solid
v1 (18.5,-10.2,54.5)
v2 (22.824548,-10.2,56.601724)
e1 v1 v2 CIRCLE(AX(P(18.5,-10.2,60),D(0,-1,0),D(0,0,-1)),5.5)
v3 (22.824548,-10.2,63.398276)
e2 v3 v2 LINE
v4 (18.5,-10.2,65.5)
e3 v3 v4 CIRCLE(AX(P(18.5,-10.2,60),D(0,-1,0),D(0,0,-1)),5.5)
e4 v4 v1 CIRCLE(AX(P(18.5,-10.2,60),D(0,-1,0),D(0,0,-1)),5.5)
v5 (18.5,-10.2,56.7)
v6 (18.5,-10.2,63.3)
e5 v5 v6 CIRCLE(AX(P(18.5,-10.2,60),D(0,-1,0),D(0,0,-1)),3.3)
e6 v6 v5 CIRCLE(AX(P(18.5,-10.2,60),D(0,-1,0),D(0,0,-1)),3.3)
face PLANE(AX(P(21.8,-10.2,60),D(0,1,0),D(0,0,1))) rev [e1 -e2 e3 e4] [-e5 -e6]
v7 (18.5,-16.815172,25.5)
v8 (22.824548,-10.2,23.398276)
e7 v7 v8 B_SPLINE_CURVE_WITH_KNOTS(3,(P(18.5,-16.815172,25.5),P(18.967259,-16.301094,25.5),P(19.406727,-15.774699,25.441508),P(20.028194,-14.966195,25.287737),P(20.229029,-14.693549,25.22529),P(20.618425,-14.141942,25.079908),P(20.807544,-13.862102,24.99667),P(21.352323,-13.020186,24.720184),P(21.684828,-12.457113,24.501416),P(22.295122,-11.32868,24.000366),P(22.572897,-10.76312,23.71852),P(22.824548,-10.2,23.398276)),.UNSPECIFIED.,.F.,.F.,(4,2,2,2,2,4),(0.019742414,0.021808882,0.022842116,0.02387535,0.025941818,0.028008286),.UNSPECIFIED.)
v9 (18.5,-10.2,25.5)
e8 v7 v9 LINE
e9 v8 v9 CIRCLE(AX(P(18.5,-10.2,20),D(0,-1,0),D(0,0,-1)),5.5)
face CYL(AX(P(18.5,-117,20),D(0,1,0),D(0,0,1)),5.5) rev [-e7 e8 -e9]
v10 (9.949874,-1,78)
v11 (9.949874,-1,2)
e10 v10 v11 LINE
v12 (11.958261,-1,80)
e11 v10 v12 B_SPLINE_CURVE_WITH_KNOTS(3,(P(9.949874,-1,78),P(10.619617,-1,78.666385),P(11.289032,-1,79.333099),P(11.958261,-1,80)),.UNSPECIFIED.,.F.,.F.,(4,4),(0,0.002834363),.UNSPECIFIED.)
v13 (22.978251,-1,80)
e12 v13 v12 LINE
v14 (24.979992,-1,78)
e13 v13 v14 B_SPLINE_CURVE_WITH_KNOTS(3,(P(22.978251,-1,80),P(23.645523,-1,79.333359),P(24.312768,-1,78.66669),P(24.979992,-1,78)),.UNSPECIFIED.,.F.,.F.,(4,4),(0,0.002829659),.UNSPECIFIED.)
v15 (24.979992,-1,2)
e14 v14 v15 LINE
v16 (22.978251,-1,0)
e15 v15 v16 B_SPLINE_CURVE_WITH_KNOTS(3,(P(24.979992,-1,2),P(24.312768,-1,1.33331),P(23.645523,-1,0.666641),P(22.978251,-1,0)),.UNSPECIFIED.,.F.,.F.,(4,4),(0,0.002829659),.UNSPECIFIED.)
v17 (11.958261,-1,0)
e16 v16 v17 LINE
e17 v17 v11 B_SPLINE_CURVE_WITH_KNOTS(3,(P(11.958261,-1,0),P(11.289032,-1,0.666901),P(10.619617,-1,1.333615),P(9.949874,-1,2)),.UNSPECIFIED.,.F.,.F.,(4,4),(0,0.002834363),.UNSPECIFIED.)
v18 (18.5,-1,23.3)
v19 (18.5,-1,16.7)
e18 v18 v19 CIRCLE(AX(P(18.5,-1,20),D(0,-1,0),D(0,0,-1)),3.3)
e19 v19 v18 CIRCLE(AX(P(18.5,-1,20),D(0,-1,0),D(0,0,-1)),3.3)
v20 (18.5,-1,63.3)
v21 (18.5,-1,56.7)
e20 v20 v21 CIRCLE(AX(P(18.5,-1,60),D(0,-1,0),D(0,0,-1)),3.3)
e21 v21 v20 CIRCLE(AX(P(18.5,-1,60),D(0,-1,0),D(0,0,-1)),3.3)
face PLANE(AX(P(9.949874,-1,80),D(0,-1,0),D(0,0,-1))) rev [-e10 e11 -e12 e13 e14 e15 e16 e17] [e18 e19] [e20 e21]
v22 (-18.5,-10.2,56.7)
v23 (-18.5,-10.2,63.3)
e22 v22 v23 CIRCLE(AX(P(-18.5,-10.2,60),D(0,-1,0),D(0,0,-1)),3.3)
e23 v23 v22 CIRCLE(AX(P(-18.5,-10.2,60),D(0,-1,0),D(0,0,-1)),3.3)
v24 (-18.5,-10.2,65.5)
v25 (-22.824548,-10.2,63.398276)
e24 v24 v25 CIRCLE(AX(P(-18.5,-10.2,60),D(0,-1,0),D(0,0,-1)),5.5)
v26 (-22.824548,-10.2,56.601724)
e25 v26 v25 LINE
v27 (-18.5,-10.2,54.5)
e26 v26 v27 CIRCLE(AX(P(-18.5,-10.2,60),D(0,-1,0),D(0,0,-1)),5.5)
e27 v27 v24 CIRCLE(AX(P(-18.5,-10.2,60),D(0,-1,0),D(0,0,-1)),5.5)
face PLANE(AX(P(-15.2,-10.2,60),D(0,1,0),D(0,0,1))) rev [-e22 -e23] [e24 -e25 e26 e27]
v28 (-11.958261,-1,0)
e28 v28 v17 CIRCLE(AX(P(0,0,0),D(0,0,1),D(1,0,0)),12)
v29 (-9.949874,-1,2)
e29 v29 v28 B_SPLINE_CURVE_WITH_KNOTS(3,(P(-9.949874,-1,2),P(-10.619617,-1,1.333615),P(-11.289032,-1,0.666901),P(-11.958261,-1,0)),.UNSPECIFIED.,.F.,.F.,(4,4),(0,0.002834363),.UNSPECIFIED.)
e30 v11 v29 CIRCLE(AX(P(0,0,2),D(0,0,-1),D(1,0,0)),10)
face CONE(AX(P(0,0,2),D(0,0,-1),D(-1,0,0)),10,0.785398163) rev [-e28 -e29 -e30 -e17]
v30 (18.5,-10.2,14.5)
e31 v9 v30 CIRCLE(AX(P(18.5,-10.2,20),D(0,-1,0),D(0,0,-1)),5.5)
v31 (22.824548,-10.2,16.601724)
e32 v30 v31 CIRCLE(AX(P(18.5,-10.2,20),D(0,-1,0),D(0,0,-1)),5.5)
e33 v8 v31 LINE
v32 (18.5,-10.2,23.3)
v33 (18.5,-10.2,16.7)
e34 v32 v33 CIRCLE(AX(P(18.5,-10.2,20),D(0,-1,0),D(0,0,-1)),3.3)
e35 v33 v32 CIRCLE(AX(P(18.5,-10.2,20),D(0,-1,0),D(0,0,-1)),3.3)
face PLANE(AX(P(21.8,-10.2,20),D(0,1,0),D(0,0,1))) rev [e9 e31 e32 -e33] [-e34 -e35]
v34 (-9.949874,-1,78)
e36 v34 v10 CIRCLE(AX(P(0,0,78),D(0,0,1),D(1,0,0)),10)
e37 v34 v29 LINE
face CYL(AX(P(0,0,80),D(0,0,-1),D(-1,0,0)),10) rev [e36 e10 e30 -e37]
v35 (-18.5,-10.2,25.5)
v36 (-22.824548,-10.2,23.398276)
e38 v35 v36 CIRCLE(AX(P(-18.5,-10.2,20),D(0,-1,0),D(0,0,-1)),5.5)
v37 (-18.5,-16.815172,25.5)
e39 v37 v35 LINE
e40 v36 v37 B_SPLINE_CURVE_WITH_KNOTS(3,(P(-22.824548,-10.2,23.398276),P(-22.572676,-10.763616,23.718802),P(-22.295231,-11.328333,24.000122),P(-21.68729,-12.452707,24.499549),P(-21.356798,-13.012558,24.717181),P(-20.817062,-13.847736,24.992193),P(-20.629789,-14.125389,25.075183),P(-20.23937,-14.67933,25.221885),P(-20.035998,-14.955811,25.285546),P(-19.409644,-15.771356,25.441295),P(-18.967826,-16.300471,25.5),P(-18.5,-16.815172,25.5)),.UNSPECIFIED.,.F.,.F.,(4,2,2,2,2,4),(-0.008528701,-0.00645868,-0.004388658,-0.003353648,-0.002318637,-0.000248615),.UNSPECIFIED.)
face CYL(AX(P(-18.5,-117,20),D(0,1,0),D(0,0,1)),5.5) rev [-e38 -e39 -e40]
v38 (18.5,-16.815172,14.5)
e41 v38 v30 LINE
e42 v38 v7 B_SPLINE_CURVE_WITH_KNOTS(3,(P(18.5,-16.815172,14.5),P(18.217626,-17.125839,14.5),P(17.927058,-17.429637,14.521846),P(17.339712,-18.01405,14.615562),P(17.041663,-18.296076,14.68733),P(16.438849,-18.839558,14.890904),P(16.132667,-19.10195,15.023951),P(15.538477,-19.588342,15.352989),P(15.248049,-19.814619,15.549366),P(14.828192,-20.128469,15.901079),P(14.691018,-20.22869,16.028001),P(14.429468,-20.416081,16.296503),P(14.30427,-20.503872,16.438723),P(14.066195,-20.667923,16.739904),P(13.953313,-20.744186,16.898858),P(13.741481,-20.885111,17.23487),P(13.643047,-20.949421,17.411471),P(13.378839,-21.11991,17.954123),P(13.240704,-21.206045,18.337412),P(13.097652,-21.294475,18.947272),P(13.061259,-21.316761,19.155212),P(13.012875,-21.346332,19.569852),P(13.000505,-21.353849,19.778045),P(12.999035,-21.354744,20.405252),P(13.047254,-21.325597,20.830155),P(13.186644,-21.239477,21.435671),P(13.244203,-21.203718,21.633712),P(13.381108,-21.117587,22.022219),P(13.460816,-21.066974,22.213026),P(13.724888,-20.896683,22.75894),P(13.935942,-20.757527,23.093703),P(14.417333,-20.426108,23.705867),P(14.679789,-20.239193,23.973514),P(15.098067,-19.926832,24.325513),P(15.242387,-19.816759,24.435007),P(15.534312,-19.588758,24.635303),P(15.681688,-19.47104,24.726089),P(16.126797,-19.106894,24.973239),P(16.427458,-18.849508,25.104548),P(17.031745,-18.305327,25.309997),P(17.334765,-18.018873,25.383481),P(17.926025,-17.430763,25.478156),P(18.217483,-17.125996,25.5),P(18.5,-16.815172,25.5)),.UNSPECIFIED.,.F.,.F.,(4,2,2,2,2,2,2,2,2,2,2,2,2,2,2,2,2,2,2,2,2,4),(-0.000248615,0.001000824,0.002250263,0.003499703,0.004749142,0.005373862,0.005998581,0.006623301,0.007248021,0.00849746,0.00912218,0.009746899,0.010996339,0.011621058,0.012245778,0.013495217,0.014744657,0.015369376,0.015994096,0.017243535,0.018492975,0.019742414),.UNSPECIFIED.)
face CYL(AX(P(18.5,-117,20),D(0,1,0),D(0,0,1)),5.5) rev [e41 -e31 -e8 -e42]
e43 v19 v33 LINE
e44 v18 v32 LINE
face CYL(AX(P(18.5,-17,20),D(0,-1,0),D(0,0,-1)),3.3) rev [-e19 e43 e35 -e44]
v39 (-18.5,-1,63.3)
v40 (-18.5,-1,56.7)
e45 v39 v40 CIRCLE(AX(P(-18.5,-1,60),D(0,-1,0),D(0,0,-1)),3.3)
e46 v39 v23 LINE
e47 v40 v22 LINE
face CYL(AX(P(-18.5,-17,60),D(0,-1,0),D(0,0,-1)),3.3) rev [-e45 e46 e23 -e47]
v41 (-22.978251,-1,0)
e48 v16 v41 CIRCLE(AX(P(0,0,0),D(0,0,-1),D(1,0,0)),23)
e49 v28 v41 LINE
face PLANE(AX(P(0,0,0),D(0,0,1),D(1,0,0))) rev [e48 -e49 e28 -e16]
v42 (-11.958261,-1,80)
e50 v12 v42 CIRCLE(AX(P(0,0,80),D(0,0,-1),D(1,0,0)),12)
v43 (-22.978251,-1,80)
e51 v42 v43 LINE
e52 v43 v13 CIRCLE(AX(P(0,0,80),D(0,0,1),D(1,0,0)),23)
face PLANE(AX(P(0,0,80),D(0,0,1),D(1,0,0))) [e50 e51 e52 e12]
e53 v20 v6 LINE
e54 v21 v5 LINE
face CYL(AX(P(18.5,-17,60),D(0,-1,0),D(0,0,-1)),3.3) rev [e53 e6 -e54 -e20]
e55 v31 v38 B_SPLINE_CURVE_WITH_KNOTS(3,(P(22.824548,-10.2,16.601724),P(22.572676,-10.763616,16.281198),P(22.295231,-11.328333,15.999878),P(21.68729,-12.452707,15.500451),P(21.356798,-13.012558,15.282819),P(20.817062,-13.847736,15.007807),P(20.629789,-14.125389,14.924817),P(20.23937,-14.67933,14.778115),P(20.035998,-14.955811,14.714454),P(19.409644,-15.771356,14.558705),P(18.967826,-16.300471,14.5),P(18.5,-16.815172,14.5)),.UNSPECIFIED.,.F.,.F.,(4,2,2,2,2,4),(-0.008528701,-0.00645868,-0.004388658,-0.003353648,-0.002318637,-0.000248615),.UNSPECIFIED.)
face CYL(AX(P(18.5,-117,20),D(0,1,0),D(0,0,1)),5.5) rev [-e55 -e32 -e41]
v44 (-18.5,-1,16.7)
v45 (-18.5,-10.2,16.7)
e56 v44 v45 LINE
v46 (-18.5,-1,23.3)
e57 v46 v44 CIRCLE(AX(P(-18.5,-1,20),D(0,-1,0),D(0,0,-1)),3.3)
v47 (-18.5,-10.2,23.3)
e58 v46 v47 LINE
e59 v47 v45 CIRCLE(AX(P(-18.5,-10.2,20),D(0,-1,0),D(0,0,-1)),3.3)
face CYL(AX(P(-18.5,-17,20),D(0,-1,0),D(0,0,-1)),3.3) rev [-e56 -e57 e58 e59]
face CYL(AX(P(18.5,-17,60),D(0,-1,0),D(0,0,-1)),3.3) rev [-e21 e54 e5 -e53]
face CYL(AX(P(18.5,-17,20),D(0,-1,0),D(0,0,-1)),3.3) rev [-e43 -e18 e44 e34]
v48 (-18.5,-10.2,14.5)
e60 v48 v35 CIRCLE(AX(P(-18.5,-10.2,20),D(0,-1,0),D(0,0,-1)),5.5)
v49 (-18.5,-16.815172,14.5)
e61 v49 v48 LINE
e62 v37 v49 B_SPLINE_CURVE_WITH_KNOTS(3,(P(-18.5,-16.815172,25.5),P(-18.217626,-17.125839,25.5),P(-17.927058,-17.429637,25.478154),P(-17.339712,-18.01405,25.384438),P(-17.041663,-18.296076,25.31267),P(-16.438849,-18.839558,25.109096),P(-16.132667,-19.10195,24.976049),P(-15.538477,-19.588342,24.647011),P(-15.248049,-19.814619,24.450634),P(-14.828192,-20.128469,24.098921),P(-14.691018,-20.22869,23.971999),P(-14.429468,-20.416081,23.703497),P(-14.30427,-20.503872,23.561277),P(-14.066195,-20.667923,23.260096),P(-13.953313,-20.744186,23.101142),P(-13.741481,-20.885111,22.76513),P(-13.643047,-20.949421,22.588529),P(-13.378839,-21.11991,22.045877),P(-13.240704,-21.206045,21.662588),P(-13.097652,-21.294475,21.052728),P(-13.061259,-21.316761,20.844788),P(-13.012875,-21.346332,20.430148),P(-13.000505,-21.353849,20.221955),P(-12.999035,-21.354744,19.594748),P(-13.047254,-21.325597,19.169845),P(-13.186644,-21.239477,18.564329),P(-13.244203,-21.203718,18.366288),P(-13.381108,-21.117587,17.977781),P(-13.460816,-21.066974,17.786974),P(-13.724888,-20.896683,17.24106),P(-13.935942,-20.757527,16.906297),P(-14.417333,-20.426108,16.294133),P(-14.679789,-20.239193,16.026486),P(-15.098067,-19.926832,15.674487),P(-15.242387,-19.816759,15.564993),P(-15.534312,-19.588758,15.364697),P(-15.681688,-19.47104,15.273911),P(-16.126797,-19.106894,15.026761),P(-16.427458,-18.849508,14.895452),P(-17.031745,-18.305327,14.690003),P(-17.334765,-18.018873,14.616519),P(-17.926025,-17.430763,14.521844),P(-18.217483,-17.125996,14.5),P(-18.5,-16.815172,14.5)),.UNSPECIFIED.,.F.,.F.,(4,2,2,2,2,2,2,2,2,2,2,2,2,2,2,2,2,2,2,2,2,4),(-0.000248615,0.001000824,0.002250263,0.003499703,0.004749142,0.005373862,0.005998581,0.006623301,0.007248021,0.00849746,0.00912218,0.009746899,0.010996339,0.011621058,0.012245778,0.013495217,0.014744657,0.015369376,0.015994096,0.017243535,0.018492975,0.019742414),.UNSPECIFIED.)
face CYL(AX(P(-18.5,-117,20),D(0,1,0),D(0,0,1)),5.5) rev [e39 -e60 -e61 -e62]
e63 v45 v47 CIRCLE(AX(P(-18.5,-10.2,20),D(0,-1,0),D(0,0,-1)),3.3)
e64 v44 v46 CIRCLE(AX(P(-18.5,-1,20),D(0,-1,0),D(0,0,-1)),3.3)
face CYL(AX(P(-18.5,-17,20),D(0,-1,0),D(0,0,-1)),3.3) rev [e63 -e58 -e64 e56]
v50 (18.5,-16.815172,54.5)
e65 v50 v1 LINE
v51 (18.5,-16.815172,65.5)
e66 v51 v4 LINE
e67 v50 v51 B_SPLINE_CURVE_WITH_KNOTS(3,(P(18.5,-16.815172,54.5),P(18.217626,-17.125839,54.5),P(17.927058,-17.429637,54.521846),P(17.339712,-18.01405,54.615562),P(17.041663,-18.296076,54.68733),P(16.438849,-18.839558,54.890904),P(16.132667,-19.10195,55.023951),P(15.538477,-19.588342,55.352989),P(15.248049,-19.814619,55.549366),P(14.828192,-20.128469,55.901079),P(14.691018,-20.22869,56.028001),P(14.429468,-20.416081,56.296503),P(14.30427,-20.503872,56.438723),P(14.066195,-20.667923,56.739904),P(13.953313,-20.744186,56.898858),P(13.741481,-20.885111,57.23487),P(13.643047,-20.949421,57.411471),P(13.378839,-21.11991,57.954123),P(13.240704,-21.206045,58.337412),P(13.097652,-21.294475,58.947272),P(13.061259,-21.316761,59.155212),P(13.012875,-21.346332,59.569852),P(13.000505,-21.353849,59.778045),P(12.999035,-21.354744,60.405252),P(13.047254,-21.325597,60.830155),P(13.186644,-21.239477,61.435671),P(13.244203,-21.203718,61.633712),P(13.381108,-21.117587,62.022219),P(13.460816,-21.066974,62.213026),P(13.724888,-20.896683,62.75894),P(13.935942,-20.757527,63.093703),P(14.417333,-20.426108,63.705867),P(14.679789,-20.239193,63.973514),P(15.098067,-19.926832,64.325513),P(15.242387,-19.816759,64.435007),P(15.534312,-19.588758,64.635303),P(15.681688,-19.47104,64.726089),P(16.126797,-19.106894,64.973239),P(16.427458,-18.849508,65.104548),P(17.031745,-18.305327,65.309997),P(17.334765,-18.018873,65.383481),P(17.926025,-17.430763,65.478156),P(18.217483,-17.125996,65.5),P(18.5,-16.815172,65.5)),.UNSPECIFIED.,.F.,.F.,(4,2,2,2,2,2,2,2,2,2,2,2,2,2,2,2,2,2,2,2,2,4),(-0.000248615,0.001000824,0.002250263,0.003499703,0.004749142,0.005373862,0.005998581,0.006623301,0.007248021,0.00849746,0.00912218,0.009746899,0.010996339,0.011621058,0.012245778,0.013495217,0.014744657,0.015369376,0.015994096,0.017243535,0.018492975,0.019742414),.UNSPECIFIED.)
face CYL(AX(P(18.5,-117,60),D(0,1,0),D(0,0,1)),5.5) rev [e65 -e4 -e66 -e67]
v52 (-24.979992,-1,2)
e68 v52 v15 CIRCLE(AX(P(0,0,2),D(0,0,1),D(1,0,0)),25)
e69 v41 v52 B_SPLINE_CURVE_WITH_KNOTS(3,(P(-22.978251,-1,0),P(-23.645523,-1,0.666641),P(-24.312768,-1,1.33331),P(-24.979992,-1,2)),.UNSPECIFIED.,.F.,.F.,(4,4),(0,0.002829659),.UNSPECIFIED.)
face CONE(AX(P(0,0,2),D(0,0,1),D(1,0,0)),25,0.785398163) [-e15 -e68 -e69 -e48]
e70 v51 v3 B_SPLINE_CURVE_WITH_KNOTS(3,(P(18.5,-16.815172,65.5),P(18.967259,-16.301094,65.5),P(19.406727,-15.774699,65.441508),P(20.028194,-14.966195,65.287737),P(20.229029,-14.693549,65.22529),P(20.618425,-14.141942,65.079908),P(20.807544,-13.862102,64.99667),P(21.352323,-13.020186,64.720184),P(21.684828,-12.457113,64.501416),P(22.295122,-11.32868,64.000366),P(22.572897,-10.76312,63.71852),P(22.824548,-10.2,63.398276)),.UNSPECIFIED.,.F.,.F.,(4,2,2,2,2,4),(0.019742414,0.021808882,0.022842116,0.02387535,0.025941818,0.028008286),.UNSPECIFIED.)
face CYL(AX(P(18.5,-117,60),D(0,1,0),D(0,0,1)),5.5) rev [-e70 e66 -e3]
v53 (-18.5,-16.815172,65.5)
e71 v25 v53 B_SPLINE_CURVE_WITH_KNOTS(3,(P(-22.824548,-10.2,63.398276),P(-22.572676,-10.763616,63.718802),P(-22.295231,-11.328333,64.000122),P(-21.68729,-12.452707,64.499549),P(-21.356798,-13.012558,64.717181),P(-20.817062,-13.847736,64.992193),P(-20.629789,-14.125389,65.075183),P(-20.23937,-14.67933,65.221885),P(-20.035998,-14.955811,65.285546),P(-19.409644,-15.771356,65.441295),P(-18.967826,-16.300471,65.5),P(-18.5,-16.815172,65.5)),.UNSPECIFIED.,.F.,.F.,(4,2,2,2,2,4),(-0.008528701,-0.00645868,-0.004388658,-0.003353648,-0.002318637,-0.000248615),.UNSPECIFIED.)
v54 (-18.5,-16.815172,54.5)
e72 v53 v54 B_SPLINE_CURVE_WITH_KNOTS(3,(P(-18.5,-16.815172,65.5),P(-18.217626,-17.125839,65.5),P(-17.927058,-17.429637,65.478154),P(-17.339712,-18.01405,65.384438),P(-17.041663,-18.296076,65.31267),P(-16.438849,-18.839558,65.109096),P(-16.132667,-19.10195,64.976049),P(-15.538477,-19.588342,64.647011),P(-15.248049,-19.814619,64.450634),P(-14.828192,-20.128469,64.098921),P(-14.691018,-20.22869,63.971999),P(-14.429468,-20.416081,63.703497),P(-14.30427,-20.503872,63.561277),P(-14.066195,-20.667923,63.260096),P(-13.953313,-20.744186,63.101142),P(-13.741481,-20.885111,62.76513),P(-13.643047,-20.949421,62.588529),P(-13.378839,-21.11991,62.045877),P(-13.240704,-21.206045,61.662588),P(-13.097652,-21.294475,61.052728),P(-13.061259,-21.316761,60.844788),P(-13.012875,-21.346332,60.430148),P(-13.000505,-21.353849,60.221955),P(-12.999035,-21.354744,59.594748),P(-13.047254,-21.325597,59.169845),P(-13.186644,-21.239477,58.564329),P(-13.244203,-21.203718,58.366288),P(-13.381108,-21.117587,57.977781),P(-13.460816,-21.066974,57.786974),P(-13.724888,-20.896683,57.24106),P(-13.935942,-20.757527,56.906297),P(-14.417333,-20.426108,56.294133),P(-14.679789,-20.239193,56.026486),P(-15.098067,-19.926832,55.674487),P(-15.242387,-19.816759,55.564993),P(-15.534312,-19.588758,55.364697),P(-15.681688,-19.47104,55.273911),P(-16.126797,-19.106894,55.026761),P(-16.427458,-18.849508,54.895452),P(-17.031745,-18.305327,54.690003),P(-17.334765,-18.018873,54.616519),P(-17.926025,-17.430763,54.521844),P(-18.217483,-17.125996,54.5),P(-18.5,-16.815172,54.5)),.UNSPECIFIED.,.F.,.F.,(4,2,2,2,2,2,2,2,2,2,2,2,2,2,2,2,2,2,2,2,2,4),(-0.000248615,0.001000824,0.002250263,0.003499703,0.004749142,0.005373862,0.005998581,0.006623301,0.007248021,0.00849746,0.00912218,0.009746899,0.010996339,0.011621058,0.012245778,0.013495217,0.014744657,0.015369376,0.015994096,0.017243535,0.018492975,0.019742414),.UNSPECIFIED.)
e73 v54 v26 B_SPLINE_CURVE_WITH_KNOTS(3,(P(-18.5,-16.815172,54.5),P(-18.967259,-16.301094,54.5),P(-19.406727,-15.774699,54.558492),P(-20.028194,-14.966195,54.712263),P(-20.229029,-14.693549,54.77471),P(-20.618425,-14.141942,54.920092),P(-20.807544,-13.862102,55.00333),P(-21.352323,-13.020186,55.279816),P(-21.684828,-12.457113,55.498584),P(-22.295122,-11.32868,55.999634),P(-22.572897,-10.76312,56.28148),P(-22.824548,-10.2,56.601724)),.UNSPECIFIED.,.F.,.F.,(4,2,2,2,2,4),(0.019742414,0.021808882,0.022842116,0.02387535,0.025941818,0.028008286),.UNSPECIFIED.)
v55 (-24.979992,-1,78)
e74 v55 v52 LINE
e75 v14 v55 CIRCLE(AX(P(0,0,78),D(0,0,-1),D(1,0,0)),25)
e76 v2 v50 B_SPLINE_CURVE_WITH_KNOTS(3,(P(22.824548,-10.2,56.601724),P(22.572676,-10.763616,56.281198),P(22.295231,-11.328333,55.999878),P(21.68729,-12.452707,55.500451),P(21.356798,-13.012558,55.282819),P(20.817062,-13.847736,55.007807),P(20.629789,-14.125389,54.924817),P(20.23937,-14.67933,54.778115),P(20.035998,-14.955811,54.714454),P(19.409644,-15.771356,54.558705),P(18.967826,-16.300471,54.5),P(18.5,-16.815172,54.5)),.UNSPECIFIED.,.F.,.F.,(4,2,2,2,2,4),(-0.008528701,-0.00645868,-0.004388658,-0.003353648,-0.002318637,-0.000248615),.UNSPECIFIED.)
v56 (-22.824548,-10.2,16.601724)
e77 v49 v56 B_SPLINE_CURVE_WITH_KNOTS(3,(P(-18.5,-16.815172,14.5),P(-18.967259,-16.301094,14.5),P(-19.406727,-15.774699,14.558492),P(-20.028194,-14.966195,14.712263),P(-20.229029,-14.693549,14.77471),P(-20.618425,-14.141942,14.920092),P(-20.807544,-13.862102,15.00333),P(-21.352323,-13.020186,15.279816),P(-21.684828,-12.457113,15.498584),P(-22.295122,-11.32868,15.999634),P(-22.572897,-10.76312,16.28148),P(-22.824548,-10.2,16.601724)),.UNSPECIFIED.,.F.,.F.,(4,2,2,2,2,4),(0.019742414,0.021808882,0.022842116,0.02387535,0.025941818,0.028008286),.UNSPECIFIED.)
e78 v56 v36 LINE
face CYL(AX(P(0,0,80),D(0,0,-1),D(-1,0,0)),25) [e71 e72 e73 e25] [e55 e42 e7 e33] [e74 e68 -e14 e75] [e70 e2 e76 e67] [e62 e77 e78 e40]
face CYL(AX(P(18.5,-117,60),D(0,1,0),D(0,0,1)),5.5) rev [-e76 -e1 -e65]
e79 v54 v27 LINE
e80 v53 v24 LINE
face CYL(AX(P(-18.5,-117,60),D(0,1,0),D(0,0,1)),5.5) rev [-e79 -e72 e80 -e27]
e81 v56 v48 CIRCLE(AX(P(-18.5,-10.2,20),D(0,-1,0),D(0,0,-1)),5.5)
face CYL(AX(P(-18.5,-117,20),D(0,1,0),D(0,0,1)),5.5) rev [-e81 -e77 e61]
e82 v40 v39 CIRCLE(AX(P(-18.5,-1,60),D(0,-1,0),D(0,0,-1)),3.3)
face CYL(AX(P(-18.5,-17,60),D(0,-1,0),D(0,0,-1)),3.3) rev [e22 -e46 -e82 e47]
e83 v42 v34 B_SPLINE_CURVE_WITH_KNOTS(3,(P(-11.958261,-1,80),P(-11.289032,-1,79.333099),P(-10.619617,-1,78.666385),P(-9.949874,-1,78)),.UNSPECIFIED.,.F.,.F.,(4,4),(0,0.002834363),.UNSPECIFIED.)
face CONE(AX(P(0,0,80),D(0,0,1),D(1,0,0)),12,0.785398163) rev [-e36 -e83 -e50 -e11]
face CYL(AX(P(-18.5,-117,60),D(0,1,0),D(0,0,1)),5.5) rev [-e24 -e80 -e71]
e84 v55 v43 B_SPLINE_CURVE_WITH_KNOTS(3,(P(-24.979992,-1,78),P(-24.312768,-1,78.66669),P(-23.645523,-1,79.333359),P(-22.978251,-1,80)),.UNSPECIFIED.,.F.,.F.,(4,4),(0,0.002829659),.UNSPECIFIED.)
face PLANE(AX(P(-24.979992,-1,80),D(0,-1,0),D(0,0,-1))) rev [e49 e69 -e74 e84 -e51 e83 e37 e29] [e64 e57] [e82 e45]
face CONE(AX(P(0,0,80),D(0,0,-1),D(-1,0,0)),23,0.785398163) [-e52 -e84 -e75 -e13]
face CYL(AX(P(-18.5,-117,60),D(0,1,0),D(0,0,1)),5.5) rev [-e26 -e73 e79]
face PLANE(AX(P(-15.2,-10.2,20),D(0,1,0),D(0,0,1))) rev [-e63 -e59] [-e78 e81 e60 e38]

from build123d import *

# Parameters (mm, degrees)
EXTRUDE_1_DEPTH           = 80
SKETCH_2_R                = 5.5
CUT_EXTRUDE_1_DEPTH       = 100
HOLE_WIZARD_1_D           = 6.6
HOLE_WIZARD_1_CBORE_D     = 11
HOLE_WIZARD_1_CBORE_DEPTH = 6.8
CHAMFER_1_SIZE            = 2


with BuildPart() as part:
    # 草图1 → 凸台-拉伸1 (new body)
    with BuildSketch(Plane.XY):
        with BuildLine():
            Line((-24.979991994, -1), (-9.949874371, -1))
            ThreePointArc((-9.949874371, -1), (0, -10), (9.949874371, -1))
            Line((9.949874371, -1), (24.979991994, -1))
            ThreePointArc((24.979991994, -1), (0, -25), (-24.979991994, -1))
        make_face()
    extrude(amount=EXTRUDE_1_DEPTH)

    # 草图2 → 切除-拉伸1 (cut)
    with BuildSketch(Plane(origin=(0, -17, 0), x_dir=(1, 0, 0), z_dir=(0, 1, 0))):
        with Locations((-18.5, -20)):
            Circle(SKETCH_2_R)
        with Locations((18.5, -20)):
            Circle(SKETCH_2_R)
        with Locations((18.5, -60)):
            Circle(SKETCH_2_R)
        with Locations((-18.5, -60)):
            Circle(SKETCH_2_R)
    extrude(amount=-CUT_EXTRUDE_1_DEPTH, mode=Mode.SUBTRACT)

    # 打孔尺寸(%根据)内六角圆柱头螺钉的类型1 (through all)
    with Locations(Plane(origin=(0, -17, 0), x_dir=(-1, 0, 0), z_dir=(0, -1, 0))):
        with Locations((-18.5, -20), (18.5, -20), (18.5, -60), (-18.5, -60)):
            CounterBoreHole(HOLE_WIZARD_1_D / 2, HOLE_WIZARD_1_CBORE_D / 2, HOLE_WIZARD_1_CBORE_DEPTH)

    # 倒角1
    chamfer_1_edges = [part.edges().sort_by_distance(p)[0] for p in [
        (0, -25, 80),
        (0, -10, 80),
        (0, -25, 0),
        (0, -10, 0),
    ]]
    chamfer(chamfer_1_edges, length=CHAMFER_1_SIZE)


solid = part.part
